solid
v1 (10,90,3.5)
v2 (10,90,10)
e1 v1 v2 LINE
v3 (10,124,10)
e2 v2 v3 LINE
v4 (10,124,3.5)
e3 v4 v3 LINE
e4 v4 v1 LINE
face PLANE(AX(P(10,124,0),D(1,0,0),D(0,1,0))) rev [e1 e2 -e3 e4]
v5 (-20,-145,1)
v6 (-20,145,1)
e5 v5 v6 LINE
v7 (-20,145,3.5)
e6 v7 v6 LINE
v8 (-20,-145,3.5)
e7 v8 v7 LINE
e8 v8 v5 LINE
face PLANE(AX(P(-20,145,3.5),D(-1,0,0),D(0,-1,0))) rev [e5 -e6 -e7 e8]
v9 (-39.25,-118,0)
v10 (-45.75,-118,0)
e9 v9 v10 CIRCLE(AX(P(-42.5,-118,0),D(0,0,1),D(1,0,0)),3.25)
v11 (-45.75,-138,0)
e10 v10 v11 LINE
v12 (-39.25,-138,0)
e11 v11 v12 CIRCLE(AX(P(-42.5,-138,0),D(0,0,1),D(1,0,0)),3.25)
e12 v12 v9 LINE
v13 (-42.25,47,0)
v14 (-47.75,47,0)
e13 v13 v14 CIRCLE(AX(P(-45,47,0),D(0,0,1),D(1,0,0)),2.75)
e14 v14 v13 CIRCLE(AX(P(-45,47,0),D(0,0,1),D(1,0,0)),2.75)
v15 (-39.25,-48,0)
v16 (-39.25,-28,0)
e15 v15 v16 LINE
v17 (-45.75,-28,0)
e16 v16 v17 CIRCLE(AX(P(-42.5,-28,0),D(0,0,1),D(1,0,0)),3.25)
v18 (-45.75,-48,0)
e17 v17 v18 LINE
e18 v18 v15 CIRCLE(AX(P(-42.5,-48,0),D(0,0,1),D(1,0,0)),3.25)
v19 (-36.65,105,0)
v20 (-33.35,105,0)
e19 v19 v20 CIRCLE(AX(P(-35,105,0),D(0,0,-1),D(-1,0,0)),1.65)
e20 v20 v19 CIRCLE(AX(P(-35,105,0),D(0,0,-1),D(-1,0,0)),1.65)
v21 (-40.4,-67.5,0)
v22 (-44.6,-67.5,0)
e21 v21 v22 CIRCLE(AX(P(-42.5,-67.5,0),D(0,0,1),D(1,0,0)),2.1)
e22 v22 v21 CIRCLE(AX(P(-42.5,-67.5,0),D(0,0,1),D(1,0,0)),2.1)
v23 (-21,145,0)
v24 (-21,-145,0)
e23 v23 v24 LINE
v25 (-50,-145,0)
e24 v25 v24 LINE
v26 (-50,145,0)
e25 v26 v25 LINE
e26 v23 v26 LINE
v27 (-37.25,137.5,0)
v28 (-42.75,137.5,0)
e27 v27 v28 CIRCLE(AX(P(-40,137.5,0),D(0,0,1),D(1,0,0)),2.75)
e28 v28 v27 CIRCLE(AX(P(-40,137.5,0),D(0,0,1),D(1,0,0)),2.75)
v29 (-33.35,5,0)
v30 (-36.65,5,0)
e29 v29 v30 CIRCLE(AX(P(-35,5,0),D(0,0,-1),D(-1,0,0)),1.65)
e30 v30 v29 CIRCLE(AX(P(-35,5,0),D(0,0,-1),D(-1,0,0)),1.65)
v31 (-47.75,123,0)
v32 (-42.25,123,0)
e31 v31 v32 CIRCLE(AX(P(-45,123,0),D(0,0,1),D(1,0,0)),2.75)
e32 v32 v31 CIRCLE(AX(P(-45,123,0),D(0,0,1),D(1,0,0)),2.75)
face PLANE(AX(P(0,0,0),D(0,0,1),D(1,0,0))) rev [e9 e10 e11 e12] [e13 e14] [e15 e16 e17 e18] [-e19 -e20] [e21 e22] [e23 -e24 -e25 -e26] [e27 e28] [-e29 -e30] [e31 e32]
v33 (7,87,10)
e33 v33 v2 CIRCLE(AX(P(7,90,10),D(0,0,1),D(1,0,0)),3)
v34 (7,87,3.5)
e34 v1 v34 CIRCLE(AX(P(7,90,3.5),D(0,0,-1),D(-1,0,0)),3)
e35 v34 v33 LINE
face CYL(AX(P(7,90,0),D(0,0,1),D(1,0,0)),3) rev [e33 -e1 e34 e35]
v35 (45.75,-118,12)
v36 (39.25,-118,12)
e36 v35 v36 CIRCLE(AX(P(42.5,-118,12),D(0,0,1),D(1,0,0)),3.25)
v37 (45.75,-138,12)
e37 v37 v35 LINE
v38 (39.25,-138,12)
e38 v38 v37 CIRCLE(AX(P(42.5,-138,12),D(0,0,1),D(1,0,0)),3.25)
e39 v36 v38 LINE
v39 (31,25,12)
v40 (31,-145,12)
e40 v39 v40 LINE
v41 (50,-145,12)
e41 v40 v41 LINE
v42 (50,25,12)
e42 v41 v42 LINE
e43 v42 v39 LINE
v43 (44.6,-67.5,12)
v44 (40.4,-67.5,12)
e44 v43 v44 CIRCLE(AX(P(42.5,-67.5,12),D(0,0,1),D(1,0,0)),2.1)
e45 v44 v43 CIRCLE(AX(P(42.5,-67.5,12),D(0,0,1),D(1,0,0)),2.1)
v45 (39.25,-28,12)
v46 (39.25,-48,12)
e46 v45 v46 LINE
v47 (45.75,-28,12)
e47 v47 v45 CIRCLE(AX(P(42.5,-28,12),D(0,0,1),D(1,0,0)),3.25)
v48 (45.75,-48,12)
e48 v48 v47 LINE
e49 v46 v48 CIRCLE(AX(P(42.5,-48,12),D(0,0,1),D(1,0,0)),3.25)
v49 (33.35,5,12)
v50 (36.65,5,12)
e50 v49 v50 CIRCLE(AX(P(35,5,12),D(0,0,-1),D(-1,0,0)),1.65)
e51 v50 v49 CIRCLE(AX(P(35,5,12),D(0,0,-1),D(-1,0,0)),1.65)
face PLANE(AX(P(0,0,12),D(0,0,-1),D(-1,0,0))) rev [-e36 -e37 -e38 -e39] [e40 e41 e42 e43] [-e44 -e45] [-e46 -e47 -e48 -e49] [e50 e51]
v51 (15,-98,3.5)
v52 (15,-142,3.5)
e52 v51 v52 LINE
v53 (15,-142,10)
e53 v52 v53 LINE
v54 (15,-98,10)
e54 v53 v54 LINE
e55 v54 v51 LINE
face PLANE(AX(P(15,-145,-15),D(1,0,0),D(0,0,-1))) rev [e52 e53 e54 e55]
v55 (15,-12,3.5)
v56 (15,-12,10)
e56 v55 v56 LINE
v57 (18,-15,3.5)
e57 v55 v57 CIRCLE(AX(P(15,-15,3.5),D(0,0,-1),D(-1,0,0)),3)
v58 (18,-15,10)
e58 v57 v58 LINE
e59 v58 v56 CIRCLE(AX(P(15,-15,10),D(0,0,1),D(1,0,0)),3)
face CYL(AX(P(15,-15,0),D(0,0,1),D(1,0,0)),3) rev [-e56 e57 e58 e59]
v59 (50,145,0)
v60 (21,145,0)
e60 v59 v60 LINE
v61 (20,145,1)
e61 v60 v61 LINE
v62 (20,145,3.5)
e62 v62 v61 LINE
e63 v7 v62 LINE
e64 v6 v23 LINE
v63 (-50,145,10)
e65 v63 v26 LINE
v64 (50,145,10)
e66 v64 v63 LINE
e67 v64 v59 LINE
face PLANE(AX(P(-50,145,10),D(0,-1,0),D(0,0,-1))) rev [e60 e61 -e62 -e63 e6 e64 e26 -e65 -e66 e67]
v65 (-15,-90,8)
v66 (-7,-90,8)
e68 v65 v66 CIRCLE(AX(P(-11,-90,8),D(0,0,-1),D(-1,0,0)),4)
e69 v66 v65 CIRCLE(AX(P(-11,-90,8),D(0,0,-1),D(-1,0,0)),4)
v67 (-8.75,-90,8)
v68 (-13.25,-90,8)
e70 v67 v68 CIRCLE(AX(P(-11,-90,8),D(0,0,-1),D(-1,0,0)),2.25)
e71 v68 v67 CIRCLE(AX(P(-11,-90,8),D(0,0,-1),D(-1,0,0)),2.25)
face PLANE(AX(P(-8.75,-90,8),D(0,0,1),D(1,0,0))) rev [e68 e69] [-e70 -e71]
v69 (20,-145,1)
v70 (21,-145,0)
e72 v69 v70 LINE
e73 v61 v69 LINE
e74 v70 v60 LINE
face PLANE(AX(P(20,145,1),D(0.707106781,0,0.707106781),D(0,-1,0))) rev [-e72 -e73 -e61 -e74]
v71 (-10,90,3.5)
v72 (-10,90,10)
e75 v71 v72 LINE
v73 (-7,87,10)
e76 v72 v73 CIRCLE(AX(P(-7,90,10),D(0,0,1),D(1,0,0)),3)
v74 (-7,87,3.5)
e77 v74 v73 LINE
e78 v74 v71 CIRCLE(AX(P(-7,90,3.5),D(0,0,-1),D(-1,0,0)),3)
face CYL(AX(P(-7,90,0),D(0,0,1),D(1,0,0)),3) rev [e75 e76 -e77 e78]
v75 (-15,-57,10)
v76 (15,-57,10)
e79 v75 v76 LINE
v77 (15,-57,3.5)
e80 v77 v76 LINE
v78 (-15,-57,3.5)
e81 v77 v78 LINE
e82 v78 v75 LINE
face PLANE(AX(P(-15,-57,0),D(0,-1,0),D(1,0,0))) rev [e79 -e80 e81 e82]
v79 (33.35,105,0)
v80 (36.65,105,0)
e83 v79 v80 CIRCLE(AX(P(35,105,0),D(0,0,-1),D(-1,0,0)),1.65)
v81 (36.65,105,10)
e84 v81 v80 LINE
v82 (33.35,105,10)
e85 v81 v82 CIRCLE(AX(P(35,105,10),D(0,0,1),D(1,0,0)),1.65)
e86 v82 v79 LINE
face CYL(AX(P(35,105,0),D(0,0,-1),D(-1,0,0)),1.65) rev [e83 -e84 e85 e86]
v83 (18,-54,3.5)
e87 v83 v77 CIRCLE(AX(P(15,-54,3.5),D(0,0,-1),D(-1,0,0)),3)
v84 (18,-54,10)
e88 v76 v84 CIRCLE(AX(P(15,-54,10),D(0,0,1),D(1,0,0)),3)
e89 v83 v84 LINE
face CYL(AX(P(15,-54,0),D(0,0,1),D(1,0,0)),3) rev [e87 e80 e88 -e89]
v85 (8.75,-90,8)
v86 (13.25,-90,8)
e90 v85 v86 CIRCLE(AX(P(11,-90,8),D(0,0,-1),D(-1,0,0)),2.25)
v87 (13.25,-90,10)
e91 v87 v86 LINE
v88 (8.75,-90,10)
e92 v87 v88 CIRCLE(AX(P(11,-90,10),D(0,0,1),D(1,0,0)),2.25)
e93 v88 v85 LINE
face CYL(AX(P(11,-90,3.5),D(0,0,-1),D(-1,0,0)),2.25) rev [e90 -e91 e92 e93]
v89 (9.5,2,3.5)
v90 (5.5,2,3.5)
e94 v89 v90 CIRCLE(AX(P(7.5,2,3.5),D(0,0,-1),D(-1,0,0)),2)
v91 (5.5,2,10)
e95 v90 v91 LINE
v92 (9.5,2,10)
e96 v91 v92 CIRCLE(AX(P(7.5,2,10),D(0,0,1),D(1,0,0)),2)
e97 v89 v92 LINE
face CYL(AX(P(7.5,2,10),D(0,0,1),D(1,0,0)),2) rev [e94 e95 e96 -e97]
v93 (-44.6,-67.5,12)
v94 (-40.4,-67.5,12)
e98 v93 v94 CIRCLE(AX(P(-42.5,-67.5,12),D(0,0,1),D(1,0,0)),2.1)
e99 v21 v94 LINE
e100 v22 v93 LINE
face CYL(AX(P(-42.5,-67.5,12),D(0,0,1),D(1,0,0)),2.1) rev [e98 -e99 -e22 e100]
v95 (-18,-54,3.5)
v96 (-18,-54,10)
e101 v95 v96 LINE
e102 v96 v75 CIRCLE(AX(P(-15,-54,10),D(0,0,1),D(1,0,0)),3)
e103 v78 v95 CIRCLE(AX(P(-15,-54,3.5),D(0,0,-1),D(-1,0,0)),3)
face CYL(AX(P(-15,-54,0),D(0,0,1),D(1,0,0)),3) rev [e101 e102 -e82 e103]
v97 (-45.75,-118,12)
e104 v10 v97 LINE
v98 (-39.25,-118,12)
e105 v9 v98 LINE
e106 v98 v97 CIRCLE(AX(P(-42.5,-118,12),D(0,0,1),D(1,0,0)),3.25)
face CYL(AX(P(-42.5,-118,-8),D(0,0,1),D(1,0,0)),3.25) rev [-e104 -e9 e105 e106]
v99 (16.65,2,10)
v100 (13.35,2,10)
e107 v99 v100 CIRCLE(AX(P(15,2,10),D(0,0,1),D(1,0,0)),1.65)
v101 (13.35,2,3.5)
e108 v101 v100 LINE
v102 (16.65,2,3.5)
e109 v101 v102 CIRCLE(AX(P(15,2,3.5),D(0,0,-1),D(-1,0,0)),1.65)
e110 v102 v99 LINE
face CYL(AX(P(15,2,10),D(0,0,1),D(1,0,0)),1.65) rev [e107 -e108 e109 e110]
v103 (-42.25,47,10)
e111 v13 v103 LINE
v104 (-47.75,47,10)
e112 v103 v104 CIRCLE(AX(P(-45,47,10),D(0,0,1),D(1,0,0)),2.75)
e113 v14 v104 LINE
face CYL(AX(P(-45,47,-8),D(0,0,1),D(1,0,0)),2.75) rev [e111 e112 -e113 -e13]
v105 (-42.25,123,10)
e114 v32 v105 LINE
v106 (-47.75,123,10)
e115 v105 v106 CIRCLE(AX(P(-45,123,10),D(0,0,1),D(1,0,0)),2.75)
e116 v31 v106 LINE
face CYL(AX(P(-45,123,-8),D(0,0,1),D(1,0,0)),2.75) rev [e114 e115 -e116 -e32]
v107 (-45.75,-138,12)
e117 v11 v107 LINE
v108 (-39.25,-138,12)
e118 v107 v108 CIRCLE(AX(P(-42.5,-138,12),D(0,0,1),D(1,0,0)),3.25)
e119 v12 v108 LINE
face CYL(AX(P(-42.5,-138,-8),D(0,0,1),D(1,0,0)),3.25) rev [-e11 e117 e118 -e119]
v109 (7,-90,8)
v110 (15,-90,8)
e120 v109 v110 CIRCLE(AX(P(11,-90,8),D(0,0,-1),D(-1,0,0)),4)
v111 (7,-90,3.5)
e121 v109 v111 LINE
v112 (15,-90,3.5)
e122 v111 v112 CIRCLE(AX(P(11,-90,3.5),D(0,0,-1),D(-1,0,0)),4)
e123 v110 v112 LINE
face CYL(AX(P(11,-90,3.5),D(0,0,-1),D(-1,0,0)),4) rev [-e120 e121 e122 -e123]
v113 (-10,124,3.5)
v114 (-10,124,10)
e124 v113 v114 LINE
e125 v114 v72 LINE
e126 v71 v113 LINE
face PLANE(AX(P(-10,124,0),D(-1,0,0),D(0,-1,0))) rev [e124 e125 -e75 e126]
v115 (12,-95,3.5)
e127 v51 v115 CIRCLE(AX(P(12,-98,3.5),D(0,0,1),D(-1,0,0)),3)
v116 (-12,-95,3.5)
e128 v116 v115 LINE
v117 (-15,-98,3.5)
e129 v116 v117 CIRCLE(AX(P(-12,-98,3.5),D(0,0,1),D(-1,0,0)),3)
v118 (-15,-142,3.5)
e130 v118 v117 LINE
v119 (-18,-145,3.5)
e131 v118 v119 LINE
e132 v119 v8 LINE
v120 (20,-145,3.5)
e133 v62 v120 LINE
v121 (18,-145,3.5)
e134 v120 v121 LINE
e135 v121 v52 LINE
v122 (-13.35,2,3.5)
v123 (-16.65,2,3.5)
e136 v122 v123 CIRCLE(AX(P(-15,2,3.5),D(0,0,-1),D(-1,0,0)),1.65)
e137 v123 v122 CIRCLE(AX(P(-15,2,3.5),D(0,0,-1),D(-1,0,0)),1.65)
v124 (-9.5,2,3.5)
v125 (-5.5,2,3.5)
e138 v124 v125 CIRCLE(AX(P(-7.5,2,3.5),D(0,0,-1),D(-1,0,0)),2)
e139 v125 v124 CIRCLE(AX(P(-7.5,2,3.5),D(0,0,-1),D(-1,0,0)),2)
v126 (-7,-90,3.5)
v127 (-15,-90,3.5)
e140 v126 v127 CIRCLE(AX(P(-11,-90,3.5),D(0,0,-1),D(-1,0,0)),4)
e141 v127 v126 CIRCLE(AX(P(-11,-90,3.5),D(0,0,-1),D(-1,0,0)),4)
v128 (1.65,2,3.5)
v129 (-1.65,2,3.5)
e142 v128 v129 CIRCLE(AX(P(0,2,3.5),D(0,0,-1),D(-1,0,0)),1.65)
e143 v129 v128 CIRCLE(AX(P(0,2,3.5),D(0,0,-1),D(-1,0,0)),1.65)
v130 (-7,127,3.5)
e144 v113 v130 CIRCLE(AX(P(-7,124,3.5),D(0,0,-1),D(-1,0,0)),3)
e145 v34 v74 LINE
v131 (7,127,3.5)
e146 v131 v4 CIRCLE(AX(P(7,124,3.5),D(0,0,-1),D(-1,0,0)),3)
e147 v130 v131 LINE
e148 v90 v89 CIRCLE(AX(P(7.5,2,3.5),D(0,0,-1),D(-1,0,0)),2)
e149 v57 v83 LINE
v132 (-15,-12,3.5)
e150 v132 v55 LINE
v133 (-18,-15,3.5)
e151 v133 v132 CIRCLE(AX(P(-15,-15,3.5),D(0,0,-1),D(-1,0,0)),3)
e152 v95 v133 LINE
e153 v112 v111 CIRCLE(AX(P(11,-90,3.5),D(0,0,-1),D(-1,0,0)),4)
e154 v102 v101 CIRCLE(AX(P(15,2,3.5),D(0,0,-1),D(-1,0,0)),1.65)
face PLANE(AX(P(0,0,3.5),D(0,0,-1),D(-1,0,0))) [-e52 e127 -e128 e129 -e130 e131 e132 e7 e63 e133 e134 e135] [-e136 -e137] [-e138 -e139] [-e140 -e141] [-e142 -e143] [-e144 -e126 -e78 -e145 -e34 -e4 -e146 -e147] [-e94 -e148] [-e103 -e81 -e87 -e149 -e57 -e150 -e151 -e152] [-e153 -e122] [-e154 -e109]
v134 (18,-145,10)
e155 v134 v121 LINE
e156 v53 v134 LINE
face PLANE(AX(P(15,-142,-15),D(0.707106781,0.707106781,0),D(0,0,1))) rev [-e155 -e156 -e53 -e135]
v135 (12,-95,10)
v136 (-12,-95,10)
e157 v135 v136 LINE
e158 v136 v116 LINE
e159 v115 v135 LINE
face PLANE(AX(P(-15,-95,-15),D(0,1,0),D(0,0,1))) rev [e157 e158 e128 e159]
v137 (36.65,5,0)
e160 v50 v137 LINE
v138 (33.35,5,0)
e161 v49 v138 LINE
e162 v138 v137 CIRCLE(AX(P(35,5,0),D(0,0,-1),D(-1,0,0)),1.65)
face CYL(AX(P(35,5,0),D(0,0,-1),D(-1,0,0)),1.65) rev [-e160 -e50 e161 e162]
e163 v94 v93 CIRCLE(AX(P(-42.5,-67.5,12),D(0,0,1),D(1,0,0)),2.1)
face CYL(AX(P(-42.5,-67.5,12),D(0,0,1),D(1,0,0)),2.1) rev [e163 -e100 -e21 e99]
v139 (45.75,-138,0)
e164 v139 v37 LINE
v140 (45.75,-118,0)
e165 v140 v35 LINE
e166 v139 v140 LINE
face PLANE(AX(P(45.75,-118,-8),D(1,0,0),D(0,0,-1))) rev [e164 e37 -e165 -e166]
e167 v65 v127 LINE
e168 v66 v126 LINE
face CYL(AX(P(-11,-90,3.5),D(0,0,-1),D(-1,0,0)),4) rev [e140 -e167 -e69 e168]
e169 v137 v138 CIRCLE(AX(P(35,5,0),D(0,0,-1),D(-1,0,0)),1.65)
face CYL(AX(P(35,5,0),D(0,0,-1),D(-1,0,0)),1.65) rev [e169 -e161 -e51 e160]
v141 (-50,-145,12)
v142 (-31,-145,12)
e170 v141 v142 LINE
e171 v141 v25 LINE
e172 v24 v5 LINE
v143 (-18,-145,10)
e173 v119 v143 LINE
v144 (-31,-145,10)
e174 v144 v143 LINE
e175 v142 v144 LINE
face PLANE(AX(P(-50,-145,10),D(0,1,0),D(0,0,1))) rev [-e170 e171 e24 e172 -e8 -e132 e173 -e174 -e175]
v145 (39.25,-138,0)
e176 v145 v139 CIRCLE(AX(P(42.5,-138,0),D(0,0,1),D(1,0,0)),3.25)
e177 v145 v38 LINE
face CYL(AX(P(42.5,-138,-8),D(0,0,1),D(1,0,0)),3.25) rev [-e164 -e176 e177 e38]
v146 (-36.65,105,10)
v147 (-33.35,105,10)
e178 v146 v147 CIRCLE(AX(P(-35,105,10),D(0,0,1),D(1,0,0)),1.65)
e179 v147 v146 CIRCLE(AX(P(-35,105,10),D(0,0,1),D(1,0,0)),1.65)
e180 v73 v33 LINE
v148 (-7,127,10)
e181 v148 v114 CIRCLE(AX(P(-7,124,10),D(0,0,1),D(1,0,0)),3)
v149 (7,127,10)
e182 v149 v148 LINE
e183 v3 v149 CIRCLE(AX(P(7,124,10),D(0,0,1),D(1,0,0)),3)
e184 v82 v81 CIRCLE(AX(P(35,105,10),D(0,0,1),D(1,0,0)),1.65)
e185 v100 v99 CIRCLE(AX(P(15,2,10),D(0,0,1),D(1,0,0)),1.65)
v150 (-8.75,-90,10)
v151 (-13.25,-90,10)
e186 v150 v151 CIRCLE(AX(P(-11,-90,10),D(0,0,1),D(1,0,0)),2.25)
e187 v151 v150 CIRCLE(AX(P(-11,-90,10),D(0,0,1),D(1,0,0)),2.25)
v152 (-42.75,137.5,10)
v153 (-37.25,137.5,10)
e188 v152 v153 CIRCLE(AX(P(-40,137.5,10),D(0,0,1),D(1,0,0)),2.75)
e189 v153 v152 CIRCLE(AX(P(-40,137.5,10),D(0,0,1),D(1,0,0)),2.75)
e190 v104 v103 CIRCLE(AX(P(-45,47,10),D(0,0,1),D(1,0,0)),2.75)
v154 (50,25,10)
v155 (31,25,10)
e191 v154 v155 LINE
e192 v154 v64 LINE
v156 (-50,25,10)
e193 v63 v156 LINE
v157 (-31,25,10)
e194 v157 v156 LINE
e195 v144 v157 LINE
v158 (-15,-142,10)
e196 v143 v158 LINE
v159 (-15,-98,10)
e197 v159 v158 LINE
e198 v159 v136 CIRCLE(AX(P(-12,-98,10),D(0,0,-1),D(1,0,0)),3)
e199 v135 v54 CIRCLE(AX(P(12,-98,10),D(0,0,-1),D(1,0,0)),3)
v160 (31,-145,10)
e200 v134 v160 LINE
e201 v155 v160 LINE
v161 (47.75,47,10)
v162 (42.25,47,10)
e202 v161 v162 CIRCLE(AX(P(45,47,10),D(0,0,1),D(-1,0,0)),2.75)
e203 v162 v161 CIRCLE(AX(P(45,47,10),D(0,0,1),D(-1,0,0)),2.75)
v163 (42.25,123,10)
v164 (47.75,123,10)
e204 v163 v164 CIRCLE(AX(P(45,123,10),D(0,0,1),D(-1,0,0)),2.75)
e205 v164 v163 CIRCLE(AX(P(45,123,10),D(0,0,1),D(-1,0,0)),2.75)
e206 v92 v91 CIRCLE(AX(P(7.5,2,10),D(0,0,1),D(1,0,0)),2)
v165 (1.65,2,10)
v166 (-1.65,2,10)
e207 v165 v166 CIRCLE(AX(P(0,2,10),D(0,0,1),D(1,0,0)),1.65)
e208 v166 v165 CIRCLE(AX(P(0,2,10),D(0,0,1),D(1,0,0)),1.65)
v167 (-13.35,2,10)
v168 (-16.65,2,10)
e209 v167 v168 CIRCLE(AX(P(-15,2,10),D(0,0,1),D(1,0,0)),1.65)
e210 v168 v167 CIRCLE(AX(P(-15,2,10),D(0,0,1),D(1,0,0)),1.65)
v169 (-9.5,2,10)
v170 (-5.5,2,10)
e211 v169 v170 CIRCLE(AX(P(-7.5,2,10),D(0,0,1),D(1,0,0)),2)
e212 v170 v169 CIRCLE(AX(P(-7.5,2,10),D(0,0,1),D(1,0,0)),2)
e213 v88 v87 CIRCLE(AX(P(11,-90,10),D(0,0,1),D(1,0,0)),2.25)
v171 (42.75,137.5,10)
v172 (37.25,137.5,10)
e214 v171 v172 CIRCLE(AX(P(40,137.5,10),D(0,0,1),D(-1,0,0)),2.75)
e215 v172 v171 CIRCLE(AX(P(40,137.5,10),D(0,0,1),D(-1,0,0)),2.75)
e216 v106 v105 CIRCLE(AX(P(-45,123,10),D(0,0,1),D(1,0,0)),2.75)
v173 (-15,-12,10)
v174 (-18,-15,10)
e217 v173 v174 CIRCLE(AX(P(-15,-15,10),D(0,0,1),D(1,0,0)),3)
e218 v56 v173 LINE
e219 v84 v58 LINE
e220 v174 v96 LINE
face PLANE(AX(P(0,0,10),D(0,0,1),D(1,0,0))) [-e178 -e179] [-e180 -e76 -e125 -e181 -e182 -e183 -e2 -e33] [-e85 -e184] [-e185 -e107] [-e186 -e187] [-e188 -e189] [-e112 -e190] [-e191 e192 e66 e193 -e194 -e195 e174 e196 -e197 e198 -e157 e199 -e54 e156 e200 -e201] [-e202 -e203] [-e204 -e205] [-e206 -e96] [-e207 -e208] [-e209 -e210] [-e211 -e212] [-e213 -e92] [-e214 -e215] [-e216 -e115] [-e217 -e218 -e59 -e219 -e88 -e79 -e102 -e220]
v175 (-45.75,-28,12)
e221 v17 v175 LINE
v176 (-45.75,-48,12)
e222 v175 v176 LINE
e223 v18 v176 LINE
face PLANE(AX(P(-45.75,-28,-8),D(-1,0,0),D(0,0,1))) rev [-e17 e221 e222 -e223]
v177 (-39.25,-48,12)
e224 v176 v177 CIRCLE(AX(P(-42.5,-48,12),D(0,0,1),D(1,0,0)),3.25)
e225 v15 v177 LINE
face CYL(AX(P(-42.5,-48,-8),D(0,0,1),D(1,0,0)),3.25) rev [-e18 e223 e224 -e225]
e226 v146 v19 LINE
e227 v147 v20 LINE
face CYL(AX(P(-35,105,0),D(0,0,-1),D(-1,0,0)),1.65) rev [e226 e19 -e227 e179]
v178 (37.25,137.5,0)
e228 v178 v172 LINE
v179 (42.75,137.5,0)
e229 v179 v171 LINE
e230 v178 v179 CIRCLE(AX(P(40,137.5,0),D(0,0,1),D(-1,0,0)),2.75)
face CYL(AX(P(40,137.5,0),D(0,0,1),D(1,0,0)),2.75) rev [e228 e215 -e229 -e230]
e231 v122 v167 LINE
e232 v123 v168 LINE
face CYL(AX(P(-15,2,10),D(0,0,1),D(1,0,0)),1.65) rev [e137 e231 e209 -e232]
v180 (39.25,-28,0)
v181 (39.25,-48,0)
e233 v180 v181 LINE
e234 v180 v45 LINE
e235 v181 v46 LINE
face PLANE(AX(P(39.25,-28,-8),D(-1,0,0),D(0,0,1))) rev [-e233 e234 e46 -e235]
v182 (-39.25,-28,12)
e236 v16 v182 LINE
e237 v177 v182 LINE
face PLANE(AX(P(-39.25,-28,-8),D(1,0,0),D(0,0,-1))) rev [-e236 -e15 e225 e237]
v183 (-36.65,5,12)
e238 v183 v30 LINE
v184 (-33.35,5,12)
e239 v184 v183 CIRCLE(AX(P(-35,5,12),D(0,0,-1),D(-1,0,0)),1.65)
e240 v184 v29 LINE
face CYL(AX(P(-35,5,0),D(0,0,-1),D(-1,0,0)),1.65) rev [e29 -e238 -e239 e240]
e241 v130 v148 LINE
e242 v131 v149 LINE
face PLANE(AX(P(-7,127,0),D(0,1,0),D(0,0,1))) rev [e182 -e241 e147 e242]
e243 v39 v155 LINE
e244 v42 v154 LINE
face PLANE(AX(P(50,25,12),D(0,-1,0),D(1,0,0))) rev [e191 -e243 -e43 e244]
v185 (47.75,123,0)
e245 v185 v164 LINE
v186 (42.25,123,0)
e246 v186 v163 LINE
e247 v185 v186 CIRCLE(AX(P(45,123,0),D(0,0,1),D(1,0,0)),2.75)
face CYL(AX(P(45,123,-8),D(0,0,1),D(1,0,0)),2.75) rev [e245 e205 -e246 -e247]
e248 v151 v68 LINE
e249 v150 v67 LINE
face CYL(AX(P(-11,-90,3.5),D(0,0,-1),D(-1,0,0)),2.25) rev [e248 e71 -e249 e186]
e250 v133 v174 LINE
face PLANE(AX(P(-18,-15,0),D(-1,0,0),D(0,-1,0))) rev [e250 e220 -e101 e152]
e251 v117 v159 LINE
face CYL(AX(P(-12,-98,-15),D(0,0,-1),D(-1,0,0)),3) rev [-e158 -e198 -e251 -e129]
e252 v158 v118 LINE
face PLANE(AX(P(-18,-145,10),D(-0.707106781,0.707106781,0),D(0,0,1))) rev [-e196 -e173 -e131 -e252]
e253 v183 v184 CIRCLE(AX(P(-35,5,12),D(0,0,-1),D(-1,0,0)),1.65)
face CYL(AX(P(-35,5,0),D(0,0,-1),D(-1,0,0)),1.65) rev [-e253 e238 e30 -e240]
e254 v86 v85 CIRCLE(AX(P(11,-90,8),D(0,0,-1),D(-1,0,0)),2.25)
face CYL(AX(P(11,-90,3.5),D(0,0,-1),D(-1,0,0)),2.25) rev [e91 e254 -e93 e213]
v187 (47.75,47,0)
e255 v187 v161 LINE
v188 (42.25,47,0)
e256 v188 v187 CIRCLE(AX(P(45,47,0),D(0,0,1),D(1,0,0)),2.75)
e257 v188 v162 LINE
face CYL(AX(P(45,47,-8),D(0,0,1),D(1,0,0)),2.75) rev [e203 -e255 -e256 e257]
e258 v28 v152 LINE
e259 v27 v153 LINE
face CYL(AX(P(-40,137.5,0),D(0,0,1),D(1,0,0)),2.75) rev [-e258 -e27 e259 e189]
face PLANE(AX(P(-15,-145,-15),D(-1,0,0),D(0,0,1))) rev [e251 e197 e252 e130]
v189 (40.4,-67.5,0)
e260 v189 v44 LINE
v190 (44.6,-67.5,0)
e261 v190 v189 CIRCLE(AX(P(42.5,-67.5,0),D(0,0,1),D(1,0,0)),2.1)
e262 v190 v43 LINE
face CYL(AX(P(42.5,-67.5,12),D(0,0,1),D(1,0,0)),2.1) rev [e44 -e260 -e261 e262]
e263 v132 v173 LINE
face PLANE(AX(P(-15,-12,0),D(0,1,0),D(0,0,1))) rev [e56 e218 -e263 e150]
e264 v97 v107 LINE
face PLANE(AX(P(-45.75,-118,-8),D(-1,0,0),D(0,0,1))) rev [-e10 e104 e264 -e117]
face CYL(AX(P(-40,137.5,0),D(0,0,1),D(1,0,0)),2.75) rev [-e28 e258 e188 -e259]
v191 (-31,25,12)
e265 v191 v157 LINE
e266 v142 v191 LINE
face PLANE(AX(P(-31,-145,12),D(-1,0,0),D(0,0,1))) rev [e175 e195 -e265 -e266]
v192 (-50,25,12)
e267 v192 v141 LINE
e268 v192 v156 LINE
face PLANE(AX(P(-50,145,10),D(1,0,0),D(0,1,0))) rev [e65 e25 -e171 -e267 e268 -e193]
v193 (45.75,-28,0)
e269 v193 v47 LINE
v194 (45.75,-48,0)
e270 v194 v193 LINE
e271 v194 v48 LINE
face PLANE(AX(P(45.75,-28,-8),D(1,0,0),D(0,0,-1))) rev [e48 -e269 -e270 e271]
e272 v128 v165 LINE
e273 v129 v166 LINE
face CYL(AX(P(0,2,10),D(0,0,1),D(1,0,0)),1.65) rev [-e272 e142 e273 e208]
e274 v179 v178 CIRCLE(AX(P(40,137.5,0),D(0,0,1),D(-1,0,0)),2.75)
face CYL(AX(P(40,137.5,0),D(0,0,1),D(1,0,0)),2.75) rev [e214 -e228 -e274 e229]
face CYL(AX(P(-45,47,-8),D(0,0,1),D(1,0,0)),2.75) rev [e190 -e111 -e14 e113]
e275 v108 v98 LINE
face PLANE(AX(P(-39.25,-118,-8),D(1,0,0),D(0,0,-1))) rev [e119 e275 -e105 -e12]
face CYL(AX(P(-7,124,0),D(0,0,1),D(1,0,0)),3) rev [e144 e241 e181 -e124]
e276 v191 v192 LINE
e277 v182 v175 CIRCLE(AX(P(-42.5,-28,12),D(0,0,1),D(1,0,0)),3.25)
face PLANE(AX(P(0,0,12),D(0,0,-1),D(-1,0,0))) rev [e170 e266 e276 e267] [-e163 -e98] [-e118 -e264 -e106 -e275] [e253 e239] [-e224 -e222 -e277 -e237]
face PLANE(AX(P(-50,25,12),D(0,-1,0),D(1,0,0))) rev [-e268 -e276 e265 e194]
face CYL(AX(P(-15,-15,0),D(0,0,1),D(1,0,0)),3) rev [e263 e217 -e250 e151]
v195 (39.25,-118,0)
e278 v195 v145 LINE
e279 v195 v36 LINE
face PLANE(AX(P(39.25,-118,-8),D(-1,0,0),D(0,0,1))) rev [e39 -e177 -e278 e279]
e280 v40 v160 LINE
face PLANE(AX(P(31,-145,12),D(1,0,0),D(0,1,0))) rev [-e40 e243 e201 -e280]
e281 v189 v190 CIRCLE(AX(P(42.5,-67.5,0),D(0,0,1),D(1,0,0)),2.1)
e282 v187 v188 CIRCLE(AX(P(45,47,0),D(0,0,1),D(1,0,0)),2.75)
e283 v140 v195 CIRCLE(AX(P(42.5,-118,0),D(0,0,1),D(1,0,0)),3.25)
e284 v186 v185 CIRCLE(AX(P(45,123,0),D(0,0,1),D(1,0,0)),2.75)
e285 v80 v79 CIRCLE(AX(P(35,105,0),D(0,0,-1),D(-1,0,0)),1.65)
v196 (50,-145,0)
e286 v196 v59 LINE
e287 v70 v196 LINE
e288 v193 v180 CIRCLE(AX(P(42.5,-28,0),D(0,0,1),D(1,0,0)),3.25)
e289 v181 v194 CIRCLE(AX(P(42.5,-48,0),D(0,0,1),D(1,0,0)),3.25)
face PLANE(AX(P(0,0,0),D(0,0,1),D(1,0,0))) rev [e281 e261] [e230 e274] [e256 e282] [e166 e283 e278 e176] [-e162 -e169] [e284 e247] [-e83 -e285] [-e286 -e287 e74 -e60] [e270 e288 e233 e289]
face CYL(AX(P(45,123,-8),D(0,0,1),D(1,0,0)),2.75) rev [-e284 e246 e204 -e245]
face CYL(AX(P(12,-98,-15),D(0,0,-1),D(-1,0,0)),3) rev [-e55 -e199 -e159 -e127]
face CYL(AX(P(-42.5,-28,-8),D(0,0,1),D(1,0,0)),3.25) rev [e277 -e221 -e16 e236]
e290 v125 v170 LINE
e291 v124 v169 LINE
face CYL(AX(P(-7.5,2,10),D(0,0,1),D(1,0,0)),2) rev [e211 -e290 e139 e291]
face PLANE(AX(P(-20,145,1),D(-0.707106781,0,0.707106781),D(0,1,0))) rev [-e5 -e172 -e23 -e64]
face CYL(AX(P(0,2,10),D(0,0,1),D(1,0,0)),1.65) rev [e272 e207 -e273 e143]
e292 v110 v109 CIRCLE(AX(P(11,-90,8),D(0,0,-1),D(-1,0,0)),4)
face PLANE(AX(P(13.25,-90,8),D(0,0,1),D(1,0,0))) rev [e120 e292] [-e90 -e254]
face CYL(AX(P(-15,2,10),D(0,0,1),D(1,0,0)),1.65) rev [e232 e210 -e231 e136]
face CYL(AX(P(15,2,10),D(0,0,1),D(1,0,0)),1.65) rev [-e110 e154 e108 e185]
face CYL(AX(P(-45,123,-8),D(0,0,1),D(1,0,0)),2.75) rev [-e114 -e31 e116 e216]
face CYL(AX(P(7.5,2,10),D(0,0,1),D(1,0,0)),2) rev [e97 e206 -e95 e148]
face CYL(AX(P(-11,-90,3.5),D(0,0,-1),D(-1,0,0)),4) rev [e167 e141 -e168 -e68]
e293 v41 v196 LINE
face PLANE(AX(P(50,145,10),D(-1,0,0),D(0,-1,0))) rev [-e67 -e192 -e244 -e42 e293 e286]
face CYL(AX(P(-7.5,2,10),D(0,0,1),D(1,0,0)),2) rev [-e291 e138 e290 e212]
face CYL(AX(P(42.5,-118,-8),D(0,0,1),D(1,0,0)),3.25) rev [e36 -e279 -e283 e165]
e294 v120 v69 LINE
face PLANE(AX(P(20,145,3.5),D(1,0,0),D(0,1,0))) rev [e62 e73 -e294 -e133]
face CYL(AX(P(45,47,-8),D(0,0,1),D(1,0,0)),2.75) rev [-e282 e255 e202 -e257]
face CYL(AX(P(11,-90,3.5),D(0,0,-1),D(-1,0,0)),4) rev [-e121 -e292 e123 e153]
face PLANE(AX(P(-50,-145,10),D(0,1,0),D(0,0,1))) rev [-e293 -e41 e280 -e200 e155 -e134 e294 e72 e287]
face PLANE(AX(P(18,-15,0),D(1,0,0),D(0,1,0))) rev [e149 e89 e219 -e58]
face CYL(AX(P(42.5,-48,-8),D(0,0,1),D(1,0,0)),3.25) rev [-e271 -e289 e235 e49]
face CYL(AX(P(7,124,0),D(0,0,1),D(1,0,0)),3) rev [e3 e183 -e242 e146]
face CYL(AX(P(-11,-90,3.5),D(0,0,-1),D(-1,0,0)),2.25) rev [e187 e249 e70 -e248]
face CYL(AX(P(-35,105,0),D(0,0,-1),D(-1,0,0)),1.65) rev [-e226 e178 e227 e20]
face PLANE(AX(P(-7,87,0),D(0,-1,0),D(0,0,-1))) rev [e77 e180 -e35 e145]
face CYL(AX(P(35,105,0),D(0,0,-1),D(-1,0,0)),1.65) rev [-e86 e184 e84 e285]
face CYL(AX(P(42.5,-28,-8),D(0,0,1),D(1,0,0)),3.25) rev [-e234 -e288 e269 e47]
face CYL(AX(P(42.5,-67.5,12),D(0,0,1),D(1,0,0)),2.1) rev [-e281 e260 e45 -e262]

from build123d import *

# Parameters (mm, degrees)
SKETCH1_W                                            = 100
SKETCH1_H                                            = 290
BOSS_EXTRUDE1_DEPTH                                  = 10
SKETCH4_W                                            = 40
SKETCH4_H                                            = 290
CUT_EXTRUDE3_DEPTH                                   = 3.5
SKETCH5_R                                            = 2.75
CUT_EXTRUDE4_DEPTH                                   = 18
LPATTERN1_COUNT                                      = 2
LPATTERN1_PITCH                                      = 76
CUT_EXTRUDE5_DEPTH                                   = 18
LPATTERN2_COUNT                                      = 2
LPATTERN2_PITCH                                      = 90
SKETCH9_W                                            = 30
SKETCH9_H                                            = 50
CUT_EXTRUDE7_DEPTH                                   = 25
BOSS_EXTRUDE3_START                                  = 2
SKETCH11_W                                           = 19
SKETCH11_H                                           = 170
BOSS_EXTRUDE3_DEPTH                                  = 2
SKETCH12_R                                           = 2.75
CUT_EXTRUDE8_DEPTH                                   = 154.704261489
CHAMFER1_SIZE                                        = 3
FILLET1_R                                            = 3
SKETCH20_R                                           = 2
CUT_EXTRUDE14_DEPTH                                  = 10
M5_TAPPED_HOLE1_D                                    = 4.2
M4_TAPPED_HOLE2_D                                    = 3.3
F_4_0_4_DIAMETER_HOLE1_D                             = 4
CUT_EXTRUDE15_DEPTH                                  = 154.704261489
CHAMFER2_SIZE                                        = 1
HOLE_SIZE_PER_SOCKET_HEAD_CAP_SCREW_TYPE_D           = 4.5
HOLE_SIZE_PER_SOCKET_HEAD_CAP_SCREW_TYPE_CBORE_D     = 8
HOLE_SIZE_PER_SOCKET_HEAD_CAP_SCREW_TYPE_CBORE_DEPTH = 4.5
CUT_EXTRUDE16_DEPTH                                  = 154.847326919
M4_TAPPED_HOLE4_D                                    = 3.3


with BuildPart() as part:
    # Sketch1 → Boss-Extrude1 (new body)
    with BuildSketch(Plane.XY):
        Rectangle(SKETCH1_W, SKETCH1_H)
    extrude(amount=BOSS_EXTRUDE1_DEPTH)

    # Sketch4 → Cut-Extrude3 (cut)
    with BuildSketch(Plane(origin=(0, 0, 0), x_dir=(-1, 0, 0), z_dir=(0, 0, -1))):
        Rectangle(SKETCH4_W, SKETCH4_H)
    extrude(amount=-CUT_EXTRUDE3_DEPTH, mode=Mode.SUBTRACT)

    # Sketch5 → Cut-Extrude4 (cut)
    with BuildSketch(Plane.XY.offset(10)):
        with Locations((-45, 123)):
            Circle(SKETCH5_R)
        with Locations((45, 123)):
            Circle(SKETCH5_R)
    cut_extrude4 = extrude(amount=-CUT_EXTRUDE4_DEPTH, mode=Mode.SUBTRACT)

    # LPattern1: Cut-Extrude4 ×2
    with Locations(*[(0, -i * LPATTERN1_PITCH, 0) for i in range(1, LPATTERN1_COUNT)]):
        add(cut_extrude4, mode=Mode.SUBTRACT)

    # Sketch6 → Cut-Extrude5 (cut)
    with BuildSketch(Plane.XY.offset(10)):
        with BuildLine():
            Line((-39.25, -28), (-39.25, -48))
            ThreePointArc((-39.25, -48), (-42.5, -51.25), (-45.75, -48))
            Line((-45.75, -48), (-45.75, -28))
            ThreePointArc((-45.75, -28), (-42.5, -24.75), (-39.25, -28))
        make_face()
        with BuildLine():
            Line((39.25, -28), (39.25, -48))
            ThreePointArc((39.25, -48), (42.5, -51.25), (45.75, -48))
            Line((45.75, -48), (45.75, -28))
            ThreePointArc((45.75, -28), (42.5, -24.75), (39.25, -28))
        make_face()
    cut_extrude5 = extrude(amount=-CUT_EXTRUDE5_DEPTH, mode=Mode.SUBTRACT)

    # LPattern2: Cut-Extrude5 ×2
    with Locations(*[(0, -i * LPATTERN2_PITCH, 0) for i in range(1, LPATTERN2_COUNT)]):
        add(cut_extrude5, mode=Mode.SUBTRACT)

    # Sketch9 → Cut-Extrude7 (cut)
    with BuildSketch(Plane.XY.offset(10)):
        with Locations((0, -120)):
            Rectangle(SKETCH9_W, SKETCH9_H)
    extrude(amount=-CUT_EXTRUDE7_DEPTH, mode=Mode.SUBTRACT)

    # Sketch11 → Boss-Extrude3 (add)
    # profile 1 of 2: a face of its own
    with BuildSketch(Plane.XY.offset(10).offset(BOSS_EXTRUDE3_START)):
        with Locations((-40.5, -60)):
            Rectangle(SKETCH11_W, SKETCH11_H)
        with BuildLine():
            Line((-39.25, -138), (-39.25, -118))
            ThreePointArc((-39.25, -118), (-42.5, -114.75), (-45.75, -118))
            Line((-45.75, -118), (-45.75, -138))
            ThreePointArc((-45.75, -138), (-42.5, -141.25), (-39.25, -138))
        make_face(mode=Mode.SUBTRACT)
        with BuildLine():
            Line((-39.25, -48), (-39.25, -28))
            ThreePointArc((-39.25, -28), (-42.5, -24.75), (-45.75, -28))
            Line((-45.75, -28), (-45.75, -48))
            ThreePointArc((-45.75, -48), (-42.5, -51.25), (-39.25, -48))
        make_face(mode=Mode.SUBTRACT)
    # profile 2 of 2: a face of its own
    with BuildSketch(Plane.XY.offset(10).offset(BOSS_EXTRUDE3_START)):
        with Locations((40.5, -60)):
            Rectangle(SKETCH11_W, SKETCH11_H)
        with BuildLine():
            Line((45.75, -138), (45.75, -118))
            ThreePointArc((45.75, -118), (42.5, -114.75), (39.25, -118))
            Line((39.25, -118), (39.25, -138))
            ThreePointArc((39.25, -138), (42.5, -141.25), (45.75, -138))
        make_face(mode=Mode.SUBTRACT)
        with BuildLine():
            Line((45.75, -48), (45.75, -28))
            ThreePointArc((45.75, -28), (42.5, -24.75), (39.25, -28))
            Line((39.25, -28), (39.25, -48))
            ThreePointArc((39.25, -48), (42.5, -51.25), (45.75, -48))
        make_face(mode=Mode.SUBTRACT)
    extrude(amount=-BOSS_EXTRUDE3_DEPTH)

    # Sketch12 → Cut-Extrude8 (cut, through all)
    with BuildSketch(Plane.XY.offset(10)):
        with Locations((-40, 137.5)):
            Circle(SKETCH12_R)
        with Locations(Location((40, 137.5, 0), (0, 0, 180))):
            Circle(SKETCH12_R)
    extrude(amount=-CUT_EXTRUDE8_DEPTH, mode=Mode.SUBTRACT)

    # Chamfer1
    chamfer1_edges = [part.edges().sort_by_distance(p)[0] for p in [
        (15, -145, 6.75),
        (-15, -145, 6.75),
    ]]
    chamfer(chamfer1_edges, length=CHAMFER1_SIZE)

    # Fillet1
    fillet1_edges = [part.edges().sort_by_distance(p)[0] for p in [
        (15, -95, 6.75),
        (-15, -95, 6.75),
    ]]
    fillet(fillet1_edges, radius=FILLET1_R)

    # Sketch20 → Cut-Extrude14 (cut)
    with BuildSketch(Plane.XY.offset(12)):
        with Locations((-42.5, -67.5)):
            Circle(SKETCH20_R)
        with Locations(Location((42.5, -67.5, 0), (0, 0, 180))):
            Circle(SKETCH20_R)
    extrude(amount=-CUT_EXTRUDE14_DEPTH, mode=Mode.SUBTRACT)

    # M5 Tapped Hole1 (through all)
    with Locations(Plane(origin=(-42.5, -67.5, 12), x_dir=(1, 0, 0), z_dir=(0, 0, 1))):
        with Locations((0, 0), (85, 0)):
            Hole(M5_TAPPED_HOLE1_D / 2)

    # M4 Tapped Hole2 (through all)
    with Locations(Plane.XY.offset(10)):
        with Locations((-15, 2), (0, 2), (15, 2)):
            Hole(M4_TAPPED_HOLE2_D / 2)

    # Ø4.0 (4) Diameter Hole1 (through all)
    with Locations(Plane.XY.offset(10)):
        with Locations((-7.5, 2), (7.5, 2)):
            Hole(F_4_0_4_DIAMETER_HOLE1_D / 2)

    # Sketch26 → Cut-Extrude15 (cut, through all)
    with BuildSketch(Plane.XY.offset(10)):
        with BuildLine():
            Line((-7, 127), (7, 127))
            ThreePointArc((7, 127), (9.121320344, 126.121320344), (10, 124))
            Line((10, 124), (10, 90))
            ThreePointArc((10, 90), (9.121320344, 87.878679656), (7, 87))
            Line((7, 87), (-7, 87))
            ThreePointArc((-7, 87), (-9.121320344, 87.878679656), (-10, 90))
            Line((-10, 90), (-10, 124))
            ThreePointArc((-10, 124), (-9.121320344, 126.121320344), (-7, 127))
        make_face()
    extrude(amount=-CUT_EXTRUDE15_DEPTH, mode=Mode.SUBTRACT)

    # Chamfer2
    chamfer2_edges = [part.edges().sort_by_distance(p)[0] for p in [
        (20, 0, 0),
        (-20, 0, 0),
    ]]
    chamfer(chamfer2_edges, length=CHAMFER2_SIZE)

    # Hole size per socket head cap screw type1 (through all)
    with Locations(Plane(origin=(0, 0, 3.5), x_dir=(-1, 0, 0), z_dir=(0, 0, -1))):
        with Locations((-11, -90), (11, -90)):
            CounterBoreHole(HOLE_SIZE_PER_SOCKET_HEAD_CAP_SCREW_TYPE_D / 2, HOLE_SIZE_PER_SOCKET_HEAD_CAP_SCREW_TYPE_CBORE_D / 2, HOLE_SIZE_PER_SOCKET_HEAD_CAP_SCREW_TYPE_CBORE_DEPTH)

    # Sketch31 → Cut-Extrude16 (cut, through all)
    with BuildSketch(Plane.XY.offset(12)):
        with BuildLine():
            Line((-15, -12), (15, -12))
            ThreePointArc((15, -12), (17.121320344, -12.878679656), (18, -15))
            Line((18, -15), (18, -54))
            ThreePointArc((18, -54), (17.121320344, -56.121320344), (15, -57))
            Line((15, -57), (-15, -57))
            ThreePointArc((-15, -57), (-17.121320344, -56.121320344), (-18, -54))
            Line((-18, -54), (-18, -15))
            ThreePointArc((-18, -15), (-17.121320344, -12.878679656), (-15, -12))
        make_face()
    extrude(amount=-CUT_EXTRUDE16_DEPTH, mode=Mode.SUBTRACT)

    # M4 Tapped Hole4 (through all)
    with Locations(Plane(origin=(0, 0, 0), x_dir=(-1, 0, 0), z_dir=(0, 0, -1))):
        with Locations((-35, 105), (35, 105), (35, 5), (-35, 5)):
            Hole(M4_TAPPED_HOLE4_D / 2)


solid = part.part
